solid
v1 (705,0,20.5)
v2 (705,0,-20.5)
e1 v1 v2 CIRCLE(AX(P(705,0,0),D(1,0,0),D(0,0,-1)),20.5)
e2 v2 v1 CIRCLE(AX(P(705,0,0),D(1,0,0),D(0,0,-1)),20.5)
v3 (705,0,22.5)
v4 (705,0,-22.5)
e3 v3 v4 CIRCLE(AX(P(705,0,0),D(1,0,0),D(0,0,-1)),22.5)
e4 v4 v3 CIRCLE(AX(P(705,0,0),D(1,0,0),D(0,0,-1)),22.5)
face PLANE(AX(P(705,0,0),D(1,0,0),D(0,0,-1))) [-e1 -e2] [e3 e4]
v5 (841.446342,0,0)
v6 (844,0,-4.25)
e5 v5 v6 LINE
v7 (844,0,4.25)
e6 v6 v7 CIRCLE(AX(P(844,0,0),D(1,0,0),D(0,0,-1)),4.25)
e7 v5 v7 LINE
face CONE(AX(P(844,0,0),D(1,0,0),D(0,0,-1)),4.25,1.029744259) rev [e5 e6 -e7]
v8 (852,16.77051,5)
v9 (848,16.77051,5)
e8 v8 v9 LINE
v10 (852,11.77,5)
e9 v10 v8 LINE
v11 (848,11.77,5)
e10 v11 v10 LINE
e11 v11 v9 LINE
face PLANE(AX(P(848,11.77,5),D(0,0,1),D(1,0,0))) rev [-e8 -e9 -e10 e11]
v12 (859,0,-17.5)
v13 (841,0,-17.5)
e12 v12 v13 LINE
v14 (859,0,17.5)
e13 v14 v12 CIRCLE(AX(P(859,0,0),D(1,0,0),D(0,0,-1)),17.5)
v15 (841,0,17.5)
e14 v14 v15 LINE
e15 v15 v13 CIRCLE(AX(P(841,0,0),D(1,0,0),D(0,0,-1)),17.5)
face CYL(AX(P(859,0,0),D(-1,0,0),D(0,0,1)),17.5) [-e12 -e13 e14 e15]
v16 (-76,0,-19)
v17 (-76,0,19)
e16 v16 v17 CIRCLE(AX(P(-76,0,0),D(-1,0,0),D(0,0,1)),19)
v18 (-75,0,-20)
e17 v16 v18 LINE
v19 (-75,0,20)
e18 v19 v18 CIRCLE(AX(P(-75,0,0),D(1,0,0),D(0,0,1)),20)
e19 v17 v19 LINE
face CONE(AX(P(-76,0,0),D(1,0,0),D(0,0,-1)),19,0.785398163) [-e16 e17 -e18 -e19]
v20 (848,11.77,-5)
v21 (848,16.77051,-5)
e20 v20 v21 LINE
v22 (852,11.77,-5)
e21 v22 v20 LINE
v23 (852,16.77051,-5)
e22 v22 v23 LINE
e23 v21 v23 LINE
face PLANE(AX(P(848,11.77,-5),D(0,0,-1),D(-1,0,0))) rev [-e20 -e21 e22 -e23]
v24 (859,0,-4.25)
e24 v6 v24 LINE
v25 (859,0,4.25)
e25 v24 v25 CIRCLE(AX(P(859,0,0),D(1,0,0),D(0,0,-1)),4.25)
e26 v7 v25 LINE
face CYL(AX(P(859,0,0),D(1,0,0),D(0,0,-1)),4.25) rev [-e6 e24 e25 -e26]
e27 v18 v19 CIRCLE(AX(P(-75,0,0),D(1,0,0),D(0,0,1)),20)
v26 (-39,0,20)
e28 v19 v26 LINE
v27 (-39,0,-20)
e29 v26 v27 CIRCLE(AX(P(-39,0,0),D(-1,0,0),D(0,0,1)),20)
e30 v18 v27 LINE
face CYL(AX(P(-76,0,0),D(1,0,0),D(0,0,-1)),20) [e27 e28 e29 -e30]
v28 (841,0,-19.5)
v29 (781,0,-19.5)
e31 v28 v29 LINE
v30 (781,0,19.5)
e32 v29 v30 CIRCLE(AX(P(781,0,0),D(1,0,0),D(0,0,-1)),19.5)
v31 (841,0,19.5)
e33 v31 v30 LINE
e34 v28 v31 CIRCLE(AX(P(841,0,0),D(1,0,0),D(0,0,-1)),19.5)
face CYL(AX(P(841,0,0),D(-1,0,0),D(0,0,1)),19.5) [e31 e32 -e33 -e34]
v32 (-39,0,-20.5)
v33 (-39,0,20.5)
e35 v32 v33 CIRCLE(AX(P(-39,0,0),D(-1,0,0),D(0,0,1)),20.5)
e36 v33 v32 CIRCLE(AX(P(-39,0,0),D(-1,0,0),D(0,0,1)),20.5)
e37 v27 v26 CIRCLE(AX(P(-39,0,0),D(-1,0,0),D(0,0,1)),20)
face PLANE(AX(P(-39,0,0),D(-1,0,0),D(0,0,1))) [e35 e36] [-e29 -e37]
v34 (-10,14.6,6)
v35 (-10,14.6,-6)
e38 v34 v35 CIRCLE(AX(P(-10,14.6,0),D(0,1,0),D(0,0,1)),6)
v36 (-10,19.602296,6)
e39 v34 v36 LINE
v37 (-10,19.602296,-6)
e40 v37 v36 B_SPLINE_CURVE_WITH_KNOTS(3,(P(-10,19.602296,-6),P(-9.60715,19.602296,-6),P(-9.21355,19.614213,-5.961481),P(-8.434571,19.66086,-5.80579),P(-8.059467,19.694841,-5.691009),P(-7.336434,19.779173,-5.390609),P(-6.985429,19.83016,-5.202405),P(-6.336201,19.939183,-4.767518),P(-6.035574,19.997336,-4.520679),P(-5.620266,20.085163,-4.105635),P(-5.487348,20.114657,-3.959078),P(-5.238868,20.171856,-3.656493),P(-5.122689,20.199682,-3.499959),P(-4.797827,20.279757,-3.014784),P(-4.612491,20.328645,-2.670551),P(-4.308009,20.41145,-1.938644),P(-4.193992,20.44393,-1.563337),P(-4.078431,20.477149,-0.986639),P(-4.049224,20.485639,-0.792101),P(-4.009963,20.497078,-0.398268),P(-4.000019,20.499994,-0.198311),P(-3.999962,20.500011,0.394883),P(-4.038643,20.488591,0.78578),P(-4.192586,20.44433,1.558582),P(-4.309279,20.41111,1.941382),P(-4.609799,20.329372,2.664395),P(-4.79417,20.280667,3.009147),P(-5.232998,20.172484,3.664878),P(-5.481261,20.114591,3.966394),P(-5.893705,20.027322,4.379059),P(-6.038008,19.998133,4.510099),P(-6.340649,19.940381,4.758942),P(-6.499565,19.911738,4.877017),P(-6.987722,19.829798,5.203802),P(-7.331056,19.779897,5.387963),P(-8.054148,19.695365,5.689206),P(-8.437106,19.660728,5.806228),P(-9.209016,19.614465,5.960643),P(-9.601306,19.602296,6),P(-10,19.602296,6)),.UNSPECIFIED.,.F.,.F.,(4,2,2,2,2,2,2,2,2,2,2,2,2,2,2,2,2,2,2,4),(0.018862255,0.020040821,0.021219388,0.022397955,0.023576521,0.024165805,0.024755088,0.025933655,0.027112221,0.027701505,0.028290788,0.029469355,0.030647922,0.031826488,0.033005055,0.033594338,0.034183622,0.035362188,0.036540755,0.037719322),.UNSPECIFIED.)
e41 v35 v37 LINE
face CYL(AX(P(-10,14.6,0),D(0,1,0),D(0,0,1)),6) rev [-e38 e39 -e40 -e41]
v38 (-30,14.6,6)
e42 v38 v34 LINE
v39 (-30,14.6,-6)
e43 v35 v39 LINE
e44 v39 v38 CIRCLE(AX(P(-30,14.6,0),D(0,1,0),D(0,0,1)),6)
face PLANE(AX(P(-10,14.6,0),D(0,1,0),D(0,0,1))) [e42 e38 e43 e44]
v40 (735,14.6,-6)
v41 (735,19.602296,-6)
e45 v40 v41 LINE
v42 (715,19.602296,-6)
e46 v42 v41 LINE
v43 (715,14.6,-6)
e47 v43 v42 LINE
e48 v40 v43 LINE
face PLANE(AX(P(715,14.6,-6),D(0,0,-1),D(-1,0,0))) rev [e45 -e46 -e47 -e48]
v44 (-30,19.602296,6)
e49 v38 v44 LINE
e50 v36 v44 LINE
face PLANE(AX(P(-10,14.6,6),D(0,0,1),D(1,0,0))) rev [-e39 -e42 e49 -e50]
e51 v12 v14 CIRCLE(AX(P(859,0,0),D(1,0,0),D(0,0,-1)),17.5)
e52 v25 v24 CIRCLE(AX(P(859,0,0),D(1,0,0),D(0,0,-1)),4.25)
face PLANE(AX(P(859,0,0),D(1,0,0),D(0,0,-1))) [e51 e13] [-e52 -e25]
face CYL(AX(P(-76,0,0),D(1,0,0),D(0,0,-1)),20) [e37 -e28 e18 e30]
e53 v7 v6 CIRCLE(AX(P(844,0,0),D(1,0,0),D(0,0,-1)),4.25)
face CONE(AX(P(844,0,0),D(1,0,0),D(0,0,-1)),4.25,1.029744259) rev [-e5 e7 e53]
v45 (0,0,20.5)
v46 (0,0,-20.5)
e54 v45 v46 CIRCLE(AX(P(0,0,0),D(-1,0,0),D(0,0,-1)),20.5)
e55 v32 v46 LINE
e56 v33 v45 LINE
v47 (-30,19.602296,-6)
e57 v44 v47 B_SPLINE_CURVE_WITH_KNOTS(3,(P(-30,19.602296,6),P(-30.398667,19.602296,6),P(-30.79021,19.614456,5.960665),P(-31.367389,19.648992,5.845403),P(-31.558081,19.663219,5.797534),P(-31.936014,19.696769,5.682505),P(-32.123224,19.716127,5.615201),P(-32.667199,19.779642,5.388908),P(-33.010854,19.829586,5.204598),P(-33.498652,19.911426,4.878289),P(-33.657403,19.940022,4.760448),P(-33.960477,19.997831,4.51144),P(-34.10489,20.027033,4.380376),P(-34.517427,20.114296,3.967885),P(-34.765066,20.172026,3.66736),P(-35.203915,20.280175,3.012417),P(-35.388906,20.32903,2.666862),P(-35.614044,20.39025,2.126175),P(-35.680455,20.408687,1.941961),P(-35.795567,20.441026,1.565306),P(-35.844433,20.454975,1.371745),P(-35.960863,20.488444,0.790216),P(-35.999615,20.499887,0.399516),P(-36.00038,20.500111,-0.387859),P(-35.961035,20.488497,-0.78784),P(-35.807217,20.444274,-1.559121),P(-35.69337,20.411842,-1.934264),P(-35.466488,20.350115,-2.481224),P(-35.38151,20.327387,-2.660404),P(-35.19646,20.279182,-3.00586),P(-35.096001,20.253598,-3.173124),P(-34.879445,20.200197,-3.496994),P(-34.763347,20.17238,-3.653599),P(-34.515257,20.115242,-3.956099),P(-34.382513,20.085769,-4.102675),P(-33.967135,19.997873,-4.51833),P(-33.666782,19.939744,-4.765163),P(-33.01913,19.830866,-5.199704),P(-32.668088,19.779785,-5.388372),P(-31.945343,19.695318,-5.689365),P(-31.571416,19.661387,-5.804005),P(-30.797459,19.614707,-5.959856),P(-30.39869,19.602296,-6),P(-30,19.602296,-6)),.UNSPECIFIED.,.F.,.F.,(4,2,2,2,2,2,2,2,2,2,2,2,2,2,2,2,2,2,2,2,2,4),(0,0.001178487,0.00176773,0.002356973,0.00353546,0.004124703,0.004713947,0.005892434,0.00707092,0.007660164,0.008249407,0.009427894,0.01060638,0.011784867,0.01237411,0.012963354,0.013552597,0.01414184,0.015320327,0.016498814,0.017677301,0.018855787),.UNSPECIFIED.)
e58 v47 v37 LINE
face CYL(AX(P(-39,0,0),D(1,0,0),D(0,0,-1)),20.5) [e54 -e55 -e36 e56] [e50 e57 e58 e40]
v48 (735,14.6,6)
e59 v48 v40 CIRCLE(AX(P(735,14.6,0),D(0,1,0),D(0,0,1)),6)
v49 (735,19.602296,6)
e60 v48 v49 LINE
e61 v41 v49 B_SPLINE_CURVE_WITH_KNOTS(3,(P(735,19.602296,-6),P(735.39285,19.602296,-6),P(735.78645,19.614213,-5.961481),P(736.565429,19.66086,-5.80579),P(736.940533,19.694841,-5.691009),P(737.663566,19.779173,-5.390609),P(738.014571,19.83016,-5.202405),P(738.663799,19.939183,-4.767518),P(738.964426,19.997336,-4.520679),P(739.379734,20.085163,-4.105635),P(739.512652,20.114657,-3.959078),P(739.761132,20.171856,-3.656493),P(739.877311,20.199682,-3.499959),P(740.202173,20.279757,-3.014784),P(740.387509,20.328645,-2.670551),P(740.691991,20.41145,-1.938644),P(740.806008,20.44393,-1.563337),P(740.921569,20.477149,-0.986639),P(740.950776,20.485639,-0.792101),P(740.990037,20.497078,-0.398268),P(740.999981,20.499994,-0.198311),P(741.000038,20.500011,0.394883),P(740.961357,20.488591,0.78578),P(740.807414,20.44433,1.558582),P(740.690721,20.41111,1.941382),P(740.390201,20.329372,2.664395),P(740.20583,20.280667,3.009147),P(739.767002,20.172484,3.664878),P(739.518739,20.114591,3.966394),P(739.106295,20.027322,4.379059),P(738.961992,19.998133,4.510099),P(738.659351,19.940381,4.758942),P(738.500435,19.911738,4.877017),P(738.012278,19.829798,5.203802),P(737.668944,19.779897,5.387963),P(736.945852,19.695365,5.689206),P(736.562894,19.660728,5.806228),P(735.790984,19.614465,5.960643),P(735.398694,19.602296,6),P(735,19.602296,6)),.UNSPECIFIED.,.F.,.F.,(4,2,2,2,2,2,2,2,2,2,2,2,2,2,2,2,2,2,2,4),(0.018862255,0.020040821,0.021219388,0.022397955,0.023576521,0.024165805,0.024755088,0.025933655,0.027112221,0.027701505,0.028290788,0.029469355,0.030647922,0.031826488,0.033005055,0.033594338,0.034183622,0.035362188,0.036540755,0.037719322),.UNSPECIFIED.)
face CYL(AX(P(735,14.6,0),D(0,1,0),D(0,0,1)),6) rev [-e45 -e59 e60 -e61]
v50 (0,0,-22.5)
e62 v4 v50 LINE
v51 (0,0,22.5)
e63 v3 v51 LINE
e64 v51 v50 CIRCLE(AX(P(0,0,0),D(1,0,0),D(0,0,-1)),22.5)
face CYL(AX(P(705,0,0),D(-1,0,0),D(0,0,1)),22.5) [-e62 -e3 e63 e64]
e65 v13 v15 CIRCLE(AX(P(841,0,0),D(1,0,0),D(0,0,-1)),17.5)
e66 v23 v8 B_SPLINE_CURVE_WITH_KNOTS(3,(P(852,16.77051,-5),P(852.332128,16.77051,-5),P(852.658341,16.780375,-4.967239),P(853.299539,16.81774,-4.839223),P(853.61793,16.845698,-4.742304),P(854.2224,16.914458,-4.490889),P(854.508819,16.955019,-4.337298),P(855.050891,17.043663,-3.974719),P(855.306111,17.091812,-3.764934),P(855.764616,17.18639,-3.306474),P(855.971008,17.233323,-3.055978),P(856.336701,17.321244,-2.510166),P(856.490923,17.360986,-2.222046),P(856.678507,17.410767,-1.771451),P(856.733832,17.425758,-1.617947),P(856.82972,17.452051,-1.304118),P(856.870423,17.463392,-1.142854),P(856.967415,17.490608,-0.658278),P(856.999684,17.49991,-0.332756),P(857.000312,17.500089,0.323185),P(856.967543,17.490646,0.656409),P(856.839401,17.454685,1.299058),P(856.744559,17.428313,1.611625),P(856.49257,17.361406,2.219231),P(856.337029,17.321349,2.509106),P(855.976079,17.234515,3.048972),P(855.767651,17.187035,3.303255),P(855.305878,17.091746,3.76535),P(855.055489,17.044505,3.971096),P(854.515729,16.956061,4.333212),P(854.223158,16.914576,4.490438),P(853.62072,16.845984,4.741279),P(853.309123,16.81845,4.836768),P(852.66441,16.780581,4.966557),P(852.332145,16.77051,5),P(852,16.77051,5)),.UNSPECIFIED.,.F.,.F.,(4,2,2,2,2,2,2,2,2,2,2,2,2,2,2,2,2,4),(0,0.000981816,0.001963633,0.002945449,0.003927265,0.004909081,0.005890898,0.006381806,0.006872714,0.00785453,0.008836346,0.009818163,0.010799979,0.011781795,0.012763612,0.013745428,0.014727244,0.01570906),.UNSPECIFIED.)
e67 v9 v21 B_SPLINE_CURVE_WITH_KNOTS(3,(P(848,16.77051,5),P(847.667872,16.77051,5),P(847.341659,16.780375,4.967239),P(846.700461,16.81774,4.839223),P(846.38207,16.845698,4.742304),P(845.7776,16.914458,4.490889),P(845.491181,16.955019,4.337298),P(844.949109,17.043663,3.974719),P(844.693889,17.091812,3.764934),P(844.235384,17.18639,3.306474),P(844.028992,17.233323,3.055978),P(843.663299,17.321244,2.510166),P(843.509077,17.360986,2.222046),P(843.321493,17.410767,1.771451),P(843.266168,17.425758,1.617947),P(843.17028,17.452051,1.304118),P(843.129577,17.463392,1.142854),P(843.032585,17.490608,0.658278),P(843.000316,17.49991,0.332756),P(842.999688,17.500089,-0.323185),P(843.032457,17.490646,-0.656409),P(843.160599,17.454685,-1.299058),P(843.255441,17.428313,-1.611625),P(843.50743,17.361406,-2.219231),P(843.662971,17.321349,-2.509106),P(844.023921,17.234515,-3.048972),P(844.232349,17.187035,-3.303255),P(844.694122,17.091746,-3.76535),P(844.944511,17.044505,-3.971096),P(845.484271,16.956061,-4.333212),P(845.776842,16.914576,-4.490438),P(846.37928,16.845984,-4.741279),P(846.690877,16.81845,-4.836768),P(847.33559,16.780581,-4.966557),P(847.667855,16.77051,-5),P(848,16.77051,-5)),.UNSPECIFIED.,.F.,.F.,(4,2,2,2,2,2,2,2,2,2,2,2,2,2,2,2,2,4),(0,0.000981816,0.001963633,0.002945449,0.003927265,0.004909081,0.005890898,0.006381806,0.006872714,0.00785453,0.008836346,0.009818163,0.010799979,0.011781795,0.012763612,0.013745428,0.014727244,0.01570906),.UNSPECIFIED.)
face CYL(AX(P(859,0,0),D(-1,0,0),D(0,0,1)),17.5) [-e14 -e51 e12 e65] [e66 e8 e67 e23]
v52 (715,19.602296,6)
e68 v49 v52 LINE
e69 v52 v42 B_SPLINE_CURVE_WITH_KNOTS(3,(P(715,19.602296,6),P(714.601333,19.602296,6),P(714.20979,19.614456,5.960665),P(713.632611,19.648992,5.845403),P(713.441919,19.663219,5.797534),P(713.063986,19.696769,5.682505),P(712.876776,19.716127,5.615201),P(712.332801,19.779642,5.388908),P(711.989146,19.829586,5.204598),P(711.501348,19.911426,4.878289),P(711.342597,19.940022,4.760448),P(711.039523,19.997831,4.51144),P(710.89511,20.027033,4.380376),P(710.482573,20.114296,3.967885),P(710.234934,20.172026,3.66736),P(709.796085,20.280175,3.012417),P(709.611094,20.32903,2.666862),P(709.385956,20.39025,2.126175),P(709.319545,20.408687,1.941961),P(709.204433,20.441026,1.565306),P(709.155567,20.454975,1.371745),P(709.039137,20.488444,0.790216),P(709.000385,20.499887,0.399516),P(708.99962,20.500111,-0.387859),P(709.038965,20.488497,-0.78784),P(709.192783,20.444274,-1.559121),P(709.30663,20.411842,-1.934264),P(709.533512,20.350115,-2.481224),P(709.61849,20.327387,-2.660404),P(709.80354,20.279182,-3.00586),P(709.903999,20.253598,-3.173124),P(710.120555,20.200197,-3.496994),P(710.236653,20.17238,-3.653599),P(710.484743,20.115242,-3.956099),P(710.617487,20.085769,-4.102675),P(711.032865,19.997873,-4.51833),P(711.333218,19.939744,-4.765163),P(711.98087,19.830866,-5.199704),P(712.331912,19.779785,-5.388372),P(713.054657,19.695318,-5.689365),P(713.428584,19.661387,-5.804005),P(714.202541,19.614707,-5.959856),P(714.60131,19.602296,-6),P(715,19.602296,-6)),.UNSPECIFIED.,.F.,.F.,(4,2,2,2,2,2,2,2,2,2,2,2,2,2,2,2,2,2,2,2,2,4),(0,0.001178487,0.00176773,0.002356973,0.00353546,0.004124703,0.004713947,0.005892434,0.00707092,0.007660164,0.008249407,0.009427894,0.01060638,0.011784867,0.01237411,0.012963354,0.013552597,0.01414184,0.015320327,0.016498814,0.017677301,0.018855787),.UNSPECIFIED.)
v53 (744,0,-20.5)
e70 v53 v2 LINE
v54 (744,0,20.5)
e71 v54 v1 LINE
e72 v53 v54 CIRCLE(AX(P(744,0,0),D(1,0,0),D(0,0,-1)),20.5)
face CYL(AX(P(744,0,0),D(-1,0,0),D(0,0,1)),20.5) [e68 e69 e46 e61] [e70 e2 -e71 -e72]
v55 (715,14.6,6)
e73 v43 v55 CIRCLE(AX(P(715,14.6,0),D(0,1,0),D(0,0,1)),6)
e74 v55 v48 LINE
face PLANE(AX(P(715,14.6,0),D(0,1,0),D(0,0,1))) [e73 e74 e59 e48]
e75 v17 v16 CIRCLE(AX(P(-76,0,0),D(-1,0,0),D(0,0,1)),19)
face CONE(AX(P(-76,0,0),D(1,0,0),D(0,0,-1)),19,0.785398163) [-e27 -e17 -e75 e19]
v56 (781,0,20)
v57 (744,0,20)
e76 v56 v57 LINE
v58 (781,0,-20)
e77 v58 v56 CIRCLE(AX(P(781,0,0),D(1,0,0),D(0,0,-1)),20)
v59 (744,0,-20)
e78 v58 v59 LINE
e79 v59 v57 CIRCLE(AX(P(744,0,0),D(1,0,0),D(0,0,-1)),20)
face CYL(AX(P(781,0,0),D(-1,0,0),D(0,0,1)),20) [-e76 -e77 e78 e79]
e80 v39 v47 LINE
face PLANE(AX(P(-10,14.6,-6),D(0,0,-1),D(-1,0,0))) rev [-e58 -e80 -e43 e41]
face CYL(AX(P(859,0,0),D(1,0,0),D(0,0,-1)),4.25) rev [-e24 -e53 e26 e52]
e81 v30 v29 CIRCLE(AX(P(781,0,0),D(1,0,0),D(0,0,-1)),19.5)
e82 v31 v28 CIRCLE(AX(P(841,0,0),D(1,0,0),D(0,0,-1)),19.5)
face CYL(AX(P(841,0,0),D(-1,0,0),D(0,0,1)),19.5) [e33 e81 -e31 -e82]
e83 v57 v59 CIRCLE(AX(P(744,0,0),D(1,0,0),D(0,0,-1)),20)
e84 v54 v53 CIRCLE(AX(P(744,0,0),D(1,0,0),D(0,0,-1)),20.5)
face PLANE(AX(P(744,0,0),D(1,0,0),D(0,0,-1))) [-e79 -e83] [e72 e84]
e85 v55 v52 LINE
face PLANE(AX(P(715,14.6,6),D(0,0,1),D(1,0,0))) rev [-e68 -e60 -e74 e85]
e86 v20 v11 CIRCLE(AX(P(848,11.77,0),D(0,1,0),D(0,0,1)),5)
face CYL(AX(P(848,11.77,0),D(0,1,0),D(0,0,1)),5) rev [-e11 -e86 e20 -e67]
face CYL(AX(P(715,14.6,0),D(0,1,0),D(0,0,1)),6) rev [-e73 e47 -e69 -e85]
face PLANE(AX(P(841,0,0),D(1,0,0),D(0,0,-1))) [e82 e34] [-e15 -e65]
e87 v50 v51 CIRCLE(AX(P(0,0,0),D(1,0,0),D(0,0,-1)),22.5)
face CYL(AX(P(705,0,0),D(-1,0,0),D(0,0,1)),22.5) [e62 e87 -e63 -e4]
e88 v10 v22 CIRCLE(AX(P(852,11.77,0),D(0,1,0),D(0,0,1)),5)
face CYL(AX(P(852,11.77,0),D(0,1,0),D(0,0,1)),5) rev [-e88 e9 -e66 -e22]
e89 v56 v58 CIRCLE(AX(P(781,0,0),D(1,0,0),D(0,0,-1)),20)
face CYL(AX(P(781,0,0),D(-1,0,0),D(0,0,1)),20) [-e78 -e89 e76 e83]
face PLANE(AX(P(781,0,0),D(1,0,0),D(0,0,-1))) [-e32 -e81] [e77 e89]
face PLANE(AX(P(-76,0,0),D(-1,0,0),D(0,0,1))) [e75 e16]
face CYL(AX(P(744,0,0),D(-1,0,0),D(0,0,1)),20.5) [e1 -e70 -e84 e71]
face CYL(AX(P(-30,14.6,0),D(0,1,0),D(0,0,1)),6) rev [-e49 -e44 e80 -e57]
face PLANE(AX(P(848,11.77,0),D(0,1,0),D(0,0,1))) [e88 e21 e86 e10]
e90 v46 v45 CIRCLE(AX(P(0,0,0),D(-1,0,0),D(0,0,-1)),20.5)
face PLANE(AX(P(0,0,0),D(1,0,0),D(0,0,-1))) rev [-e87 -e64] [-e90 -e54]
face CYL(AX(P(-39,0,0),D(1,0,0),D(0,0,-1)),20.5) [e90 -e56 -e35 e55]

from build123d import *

# Parameters (mm, degrees)
SKETCH_1_R              = 22.5
EXTRUDE_1_DEPTH         = 705
SKETCH_2_R              = 20.5
EXTRUDE_2_DEPTH         = 39
SKETCH_3_R              = 20
EXTRUDE_3_DEPTH         = 37
SKETCH_4_R              = 19.5
EXTRUDE_4_DEPTH         = 60
SKETCH_5_R              = 17.5
EXTRUDE_5_DEPTH         = 18
EXTRUDE_START           = 39
SKETCH_6_R              = 20.5
EXTRUDE_6_DEPTH         = 39
EXTRUDE_START_2         = 37
SKETCH_7_R              = 20
EXTRUDE_7_DEPTH         = 37
CHAMFER_1_SIZE          = 1
CUT_EXTRUDE_1_DEPTH     = 5.9
CUT_EXTRUDE_2_DEPTH     = 5.73
HOLE_WIZARD_M10_1_D     = 8.5
HOLE_WIZARD_M10_1_DEPTH = 15
HOLE_WIZARD_M10_1_TIP   = 2.553657631


with BuildPart() as part:
    # 草图1 → 凸台-拉伸1 (new body)
    with BuildSketch(Plane(origin=(0, 0, 0), x_dir=(0, 0, -1), z_dir=(1, 0, 0))):
        Circle(SKETCH_1_R)
    extrude(amount=EXTRUDE_1_DEPTH)

    # 草图2 → 凸台-拉伸2 (add)
    with BuildSketch(Plane(origin=(705, 0, 0), x_dir=(0, 0, -1), z_dir=(1, 0, 0))):
        Circle(SKETCH_2_R)
    extrude(amount=EXTRUDE_2_DEPTH)

    # 草图3 → 凸台-拉伸3 (add)
    with BuildSketch(Plane(origin=(744, 0, 0), x_dir=(0, 0, -1), z_dir=(1, 0, 0))):
        Circle(SKETCH_3_R)
    extrude(amount=EXTRUDE_3_DEPTH)

    # 草图4 → 凸台-拉伸4 (add)
    with BuildSketch(Plane(origin=(781, 0, 0), x_dir=(0, 0, -1), z_dir=(1, 0, 0))):
        Circle(SKETCH_4_R)
    extrude(amount=EXTRUDE_4_DEPTH)

    # 草图5 → 凸台-拉伸5 (add)
    with BuildSketch(Plane(origin=(841, 0, 0), x_dir=(0, 0, -1), z_dir=(1, 0, 0))):
        Circle(SKETCH_5_R)
    extrude(amount=EXTRUDE_5_DEPTH)

    # 草图6 → 凸台-拉伸6 (add)
    with BuildSketch(Plane.ZY.offset(EXTRUDE_START)):
        with Locations(Location((0, 0, 0), (0, 0, 180))):
            Circle(SKETCH_6_R)
    extrude(amount=-EXTRUDE_6_DEPTH)

    # 草图7 → 凸台-拉伸7 (add)
    with BuildSketch(Plane.ZY.offset(39).offset(EXTRUDE_START_2)):
        with Locations(Location((0, 0, 0), (0, 0, 180))):
            Circle(SKETCH_7_R)
    extrude(amount=-EXTRUDE_7_DEPTH)

    # 倒角1
    chamfer_1_edges = [part.edges().sort_by_distance(p)[0] for p in [
        (-76, 0, 20),
    ]]
    chamfer(chamfer_1_edges, length=CHAMFER_1_SIZE)

    # 草图8 → 切除-拉伸1 (cut)
    with BuildSketch(Plane(origin=(0, 20.5, 0), x_dir=(1, 0, 0), z_dir=(0, 1, 0))):
        with BuildLine():
            Line((-10, -6), (-30, -6))
            ThreePointArc((-30, -6), (-36, 0), (-30, 6))
            Line((-30, 6), (-10, 6))
            ThreePointArc((-10, 6), (-4, 0), (-10, -6))
        make_face()
        with BuildLine():
            Line((715, 6), (735, 6))
            ThreePointArc((735, 6), (741, 0), (735, -6))
            Line((735, -6), (715, -6))
            ThreePointArc((715, -6), (709, 0), (715, 6))
        make_face()
    extrude(amount=-CUT_EXTRUDE_1_DEPTH, mode=Mode.SUBTRACT)

    # 草图9 → 切除-拉伸2 (cut)
    with BuildSketch(Plane(origin=(0, 17.5, 0), x_dir=(1, 0, 0), z_dir=(0, 1, 0))):
        with BuildLine():
            Line((848, 5), (852, 5))
            ThreePointArc((852, 5), (857, 0), (852, -5))
            Line((852, -5), (848, -5))
            ThreePointArc((848, -5), (843, 0), (848, 5))
        make_face()
    extrude(amount=-CUT_EXTRUDE_2_DEPTH, mode=Mode.SUBTRACT)

    # M10 螺纹孔1
    with Locations(Plane(origin=(859, 0, 0), x_dir=(0, 0, -1), z_dir=(1, 0, 0))):
        with Locations((0, 0)):
            Hole(HOLE_WIZARD_M10_1_D / 2, depth=HOLE_WIZARD_M10_1_DEPTH)
            with Locations((0, 0, -(HOLE_WIZARD_M10_1_DEPTH + HOLE_WIZARD_M10_1_TIP / 2))):  # 118° drill point
                Cone(0, HOLE_WIZARD_M10_1_D / 2, HOLE_WIZARD_M10_1_TIP, mode=Mode.SUBTRACT)


solid = part.part
